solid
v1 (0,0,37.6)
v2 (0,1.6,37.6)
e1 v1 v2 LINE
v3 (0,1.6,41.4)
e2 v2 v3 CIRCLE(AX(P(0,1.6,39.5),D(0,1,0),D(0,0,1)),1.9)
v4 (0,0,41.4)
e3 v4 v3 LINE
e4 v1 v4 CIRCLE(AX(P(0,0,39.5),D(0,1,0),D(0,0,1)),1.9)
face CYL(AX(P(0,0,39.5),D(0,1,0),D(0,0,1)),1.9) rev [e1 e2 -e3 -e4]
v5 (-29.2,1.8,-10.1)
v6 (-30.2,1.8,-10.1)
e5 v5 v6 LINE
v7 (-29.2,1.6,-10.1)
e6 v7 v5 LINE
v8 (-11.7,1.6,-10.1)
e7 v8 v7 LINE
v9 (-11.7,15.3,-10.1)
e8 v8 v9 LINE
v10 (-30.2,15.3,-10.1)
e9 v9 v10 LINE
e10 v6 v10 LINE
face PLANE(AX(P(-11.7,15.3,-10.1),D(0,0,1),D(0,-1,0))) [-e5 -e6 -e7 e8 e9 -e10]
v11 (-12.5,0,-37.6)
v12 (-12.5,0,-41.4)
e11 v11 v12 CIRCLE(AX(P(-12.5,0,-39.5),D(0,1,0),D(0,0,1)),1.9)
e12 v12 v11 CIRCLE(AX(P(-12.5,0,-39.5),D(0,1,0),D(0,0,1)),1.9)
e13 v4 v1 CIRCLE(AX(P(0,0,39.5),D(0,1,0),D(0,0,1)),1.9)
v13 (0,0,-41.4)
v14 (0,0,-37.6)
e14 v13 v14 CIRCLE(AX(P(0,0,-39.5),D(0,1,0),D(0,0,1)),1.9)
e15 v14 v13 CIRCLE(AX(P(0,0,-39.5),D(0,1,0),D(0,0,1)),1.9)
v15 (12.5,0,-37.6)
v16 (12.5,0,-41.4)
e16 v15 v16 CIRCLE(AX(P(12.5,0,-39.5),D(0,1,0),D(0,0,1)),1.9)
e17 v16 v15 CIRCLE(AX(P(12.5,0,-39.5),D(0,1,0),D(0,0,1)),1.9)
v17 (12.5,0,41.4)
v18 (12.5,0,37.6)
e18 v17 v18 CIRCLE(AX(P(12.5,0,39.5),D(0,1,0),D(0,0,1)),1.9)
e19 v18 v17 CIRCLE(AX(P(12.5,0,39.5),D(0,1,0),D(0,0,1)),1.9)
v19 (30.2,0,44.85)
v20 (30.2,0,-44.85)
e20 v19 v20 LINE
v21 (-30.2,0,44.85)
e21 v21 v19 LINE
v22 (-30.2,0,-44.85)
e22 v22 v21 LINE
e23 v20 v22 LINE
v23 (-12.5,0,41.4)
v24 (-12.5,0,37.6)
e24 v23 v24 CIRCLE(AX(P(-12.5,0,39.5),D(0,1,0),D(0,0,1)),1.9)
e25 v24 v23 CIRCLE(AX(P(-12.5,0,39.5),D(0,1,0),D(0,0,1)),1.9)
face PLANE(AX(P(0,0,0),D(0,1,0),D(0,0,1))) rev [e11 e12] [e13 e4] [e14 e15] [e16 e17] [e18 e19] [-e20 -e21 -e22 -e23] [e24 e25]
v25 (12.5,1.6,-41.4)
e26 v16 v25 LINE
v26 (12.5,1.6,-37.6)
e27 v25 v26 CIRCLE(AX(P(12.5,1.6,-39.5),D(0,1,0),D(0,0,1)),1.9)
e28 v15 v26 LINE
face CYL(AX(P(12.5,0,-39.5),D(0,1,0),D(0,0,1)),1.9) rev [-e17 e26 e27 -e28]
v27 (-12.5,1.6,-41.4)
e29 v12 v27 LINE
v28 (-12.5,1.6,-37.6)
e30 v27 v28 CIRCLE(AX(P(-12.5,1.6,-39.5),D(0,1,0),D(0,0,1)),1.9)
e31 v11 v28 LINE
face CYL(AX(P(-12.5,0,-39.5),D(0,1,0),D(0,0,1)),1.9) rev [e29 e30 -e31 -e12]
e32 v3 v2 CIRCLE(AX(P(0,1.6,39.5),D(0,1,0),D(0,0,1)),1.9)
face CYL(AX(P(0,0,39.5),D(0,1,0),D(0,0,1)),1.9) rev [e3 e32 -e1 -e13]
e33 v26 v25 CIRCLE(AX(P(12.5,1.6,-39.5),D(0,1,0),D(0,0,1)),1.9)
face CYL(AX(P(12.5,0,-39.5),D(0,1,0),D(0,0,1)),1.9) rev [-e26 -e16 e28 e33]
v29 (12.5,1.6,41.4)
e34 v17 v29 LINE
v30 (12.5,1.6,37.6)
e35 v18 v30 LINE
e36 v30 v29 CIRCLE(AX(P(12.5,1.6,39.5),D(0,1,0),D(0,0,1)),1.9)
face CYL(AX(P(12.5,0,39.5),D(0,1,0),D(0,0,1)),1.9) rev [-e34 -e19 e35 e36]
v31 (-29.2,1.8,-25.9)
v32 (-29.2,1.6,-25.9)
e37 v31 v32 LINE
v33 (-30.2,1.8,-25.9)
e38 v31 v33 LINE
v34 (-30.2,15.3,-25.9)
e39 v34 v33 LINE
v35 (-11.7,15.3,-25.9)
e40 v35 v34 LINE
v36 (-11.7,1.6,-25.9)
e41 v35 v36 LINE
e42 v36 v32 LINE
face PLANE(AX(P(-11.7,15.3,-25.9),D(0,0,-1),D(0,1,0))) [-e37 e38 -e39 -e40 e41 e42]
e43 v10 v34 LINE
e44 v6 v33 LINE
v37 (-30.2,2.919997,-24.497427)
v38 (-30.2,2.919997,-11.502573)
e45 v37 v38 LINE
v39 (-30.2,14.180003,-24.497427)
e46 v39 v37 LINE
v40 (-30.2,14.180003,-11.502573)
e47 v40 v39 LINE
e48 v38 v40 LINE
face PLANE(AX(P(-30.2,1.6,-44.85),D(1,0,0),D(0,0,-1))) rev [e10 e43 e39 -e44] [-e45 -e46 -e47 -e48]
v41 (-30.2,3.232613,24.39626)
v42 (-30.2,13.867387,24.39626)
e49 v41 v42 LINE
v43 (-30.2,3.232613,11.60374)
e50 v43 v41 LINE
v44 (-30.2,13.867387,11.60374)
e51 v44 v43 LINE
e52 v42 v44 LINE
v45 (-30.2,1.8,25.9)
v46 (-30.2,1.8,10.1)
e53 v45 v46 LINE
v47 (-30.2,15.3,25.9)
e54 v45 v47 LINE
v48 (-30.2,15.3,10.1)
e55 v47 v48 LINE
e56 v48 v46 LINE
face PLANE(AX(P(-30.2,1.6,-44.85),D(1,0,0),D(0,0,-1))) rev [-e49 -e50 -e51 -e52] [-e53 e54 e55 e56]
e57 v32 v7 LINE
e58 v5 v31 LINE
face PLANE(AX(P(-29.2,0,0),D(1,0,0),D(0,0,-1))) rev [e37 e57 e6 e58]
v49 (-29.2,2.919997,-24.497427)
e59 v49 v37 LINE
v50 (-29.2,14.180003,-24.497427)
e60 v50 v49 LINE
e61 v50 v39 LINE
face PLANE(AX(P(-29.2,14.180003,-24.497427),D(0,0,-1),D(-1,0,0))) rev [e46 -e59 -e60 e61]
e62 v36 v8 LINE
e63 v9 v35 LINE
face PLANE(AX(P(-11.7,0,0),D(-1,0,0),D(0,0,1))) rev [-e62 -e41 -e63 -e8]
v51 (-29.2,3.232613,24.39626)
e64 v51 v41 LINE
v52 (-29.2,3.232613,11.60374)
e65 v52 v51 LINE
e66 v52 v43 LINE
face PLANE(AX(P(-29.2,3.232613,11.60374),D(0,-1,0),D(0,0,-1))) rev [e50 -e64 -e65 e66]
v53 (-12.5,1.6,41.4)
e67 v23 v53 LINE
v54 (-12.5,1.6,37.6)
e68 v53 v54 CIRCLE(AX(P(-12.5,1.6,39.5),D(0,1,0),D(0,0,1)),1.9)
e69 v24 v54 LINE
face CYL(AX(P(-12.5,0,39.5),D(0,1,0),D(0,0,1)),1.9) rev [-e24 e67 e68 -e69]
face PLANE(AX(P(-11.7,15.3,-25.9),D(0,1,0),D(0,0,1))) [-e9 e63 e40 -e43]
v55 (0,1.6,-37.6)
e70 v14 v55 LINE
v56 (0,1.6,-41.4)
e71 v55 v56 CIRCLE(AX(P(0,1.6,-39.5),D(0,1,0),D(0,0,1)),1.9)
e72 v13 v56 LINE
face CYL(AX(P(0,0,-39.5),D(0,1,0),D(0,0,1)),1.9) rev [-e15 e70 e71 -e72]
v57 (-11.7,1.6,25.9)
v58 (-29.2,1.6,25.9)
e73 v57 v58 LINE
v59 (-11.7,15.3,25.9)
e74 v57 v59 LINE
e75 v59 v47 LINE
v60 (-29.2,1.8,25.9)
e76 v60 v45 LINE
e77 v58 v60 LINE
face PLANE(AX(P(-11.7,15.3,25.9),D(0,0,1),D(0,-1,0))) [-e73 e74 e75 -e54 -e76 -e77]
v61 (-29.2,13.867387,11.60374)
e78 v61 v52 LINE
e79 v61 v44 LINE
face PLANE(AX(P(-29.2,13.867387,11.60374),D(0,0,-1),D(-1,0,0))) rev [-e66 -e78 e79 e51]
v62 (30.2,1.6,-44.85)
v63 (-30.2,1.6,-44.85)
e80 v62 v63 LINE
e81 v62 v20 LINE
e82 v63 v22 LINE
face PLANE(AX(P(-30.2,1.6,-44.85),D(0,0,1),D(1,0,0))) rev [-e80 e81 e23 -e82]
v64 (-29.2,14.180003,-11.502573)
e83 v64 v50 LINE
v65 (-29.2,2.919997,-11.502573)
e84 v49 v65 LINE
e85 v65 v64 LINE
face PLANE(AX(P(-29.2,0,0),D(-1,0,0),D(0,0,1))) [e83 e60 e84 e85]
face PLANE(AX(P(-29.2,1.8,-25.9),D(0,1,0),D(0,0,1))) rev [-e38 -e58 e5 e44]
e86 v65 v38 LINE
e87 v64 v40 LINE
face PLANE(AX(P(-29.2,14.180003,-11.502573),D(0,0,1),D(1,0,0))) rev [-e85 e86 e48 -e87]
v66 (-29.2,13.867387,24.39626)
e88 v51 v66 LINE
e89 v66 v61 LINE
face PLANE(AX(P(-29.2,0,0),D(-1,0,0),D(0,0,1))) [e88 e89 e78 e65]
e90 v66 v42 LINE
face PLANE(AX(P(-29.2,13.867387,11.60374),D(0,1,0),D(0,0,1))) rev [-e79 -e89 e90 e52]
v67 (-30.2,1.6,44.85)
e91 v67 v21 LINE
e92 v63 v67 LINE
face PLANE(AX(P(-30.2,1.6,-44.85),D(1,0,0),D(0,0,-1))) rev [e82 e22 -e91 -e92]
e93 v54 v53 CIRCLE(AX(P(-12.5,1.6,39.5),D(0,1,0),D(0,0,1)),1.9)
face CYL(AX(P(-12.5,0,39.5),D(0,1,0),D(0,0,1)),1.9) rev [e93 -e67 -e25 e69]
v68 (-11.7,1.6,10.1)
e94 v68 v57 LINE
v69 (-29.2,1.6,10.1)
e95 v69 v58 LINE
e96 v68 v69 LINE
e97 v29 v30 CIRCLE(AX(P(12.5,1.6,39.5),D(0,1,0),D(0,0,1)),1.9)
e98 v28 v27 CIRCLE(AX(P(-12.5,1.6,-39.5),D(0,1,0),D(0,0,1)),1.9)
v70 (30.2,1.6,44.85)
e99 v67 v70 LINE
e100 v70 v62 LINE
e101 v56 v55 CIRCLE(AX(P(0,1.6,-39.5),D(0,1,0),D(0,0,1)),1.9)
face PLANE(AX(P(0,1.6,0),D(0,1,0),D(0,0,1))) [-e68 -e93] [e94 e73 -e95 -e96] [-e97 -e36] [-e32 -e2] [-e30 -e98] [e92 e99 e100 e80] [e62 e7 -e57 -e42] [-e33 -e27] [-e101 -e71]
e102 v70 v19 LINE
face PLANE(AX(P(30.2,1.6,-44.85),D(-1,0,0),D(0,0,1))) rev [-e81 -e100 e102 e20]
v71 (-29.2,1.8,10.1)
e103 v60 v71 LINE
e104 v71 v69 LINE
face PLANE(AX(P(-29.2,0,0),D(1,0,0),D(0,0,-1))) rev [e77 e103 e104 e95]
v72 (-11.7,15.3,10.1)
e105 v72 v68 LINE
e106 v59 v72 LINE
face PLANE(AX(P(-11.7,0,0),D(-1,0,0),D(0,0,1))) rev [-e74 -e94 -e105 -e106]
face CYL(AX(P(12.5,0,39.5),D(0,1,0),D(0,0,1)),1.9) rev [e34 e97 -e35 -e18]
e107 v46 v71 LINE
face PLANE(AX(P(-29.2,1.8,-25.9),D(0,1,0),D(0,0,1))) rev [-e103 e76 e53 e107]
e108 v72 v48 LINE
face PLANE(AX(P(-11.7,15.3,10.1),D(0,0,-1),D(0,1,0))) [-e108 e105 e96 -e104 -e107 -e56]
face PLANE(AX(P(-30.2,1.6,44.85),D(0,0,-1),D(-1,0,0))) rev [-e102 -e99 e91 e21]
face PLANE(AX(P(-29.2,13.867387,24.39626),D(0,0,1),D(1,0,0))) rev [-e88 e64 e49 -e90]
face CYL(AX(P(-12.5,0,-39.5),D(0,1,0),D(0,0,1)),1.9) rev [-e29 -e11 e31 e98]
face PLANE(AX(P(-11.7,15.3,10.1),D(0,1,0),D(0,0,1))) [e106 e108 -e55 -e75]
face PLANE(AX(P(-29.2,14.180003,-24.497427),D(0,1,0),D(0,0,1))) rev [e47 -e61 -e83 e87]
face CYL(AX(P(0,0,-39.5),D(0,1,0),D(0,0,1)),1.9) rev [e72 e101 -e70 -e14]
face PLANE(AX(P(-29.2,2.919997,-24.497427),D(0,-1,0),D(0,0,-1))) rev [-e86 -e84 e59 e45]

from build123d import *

# Parameters (mm, degrees)
SKETCH_1_W          = 60.4
SKETCH_1_H          = 89.7
EXTRUDE_1_DEPTH     = 1.6
SKETCH_2_R          = 1.9
CUT_EXTRUDE_1_DEPTH = 1.6
SKETCH_3_W          = 15.8
SKETCH_3_H          = 13.7
EXTRUDE_2_DEPTH     = 18.5
SKETCH_4_W          = 51.8
SKETCH_4_H          = 0.2
CUT_EXTRUDE_2_DEPTH = 1
SKETCH_5_W          = 12.792520148
SKETCH_5_H          = 10.634773198
SKETCH_5_W_2        = 12.994853118
SKETCH_5_H_2        = 11.260006872
CUT_EXTRUDE_3_DEPTH = 1


with BuildPart() as part:
    # 草图1 → 凸台-拉伸1 (new body)
    with BuildSketch(Plane(origin=(0, 0, 0), x_dir=(1, 0, 0), z_dir=(0, 1, 0))):
        Rectangle(SKETCH_1_W, SKETCH_1_H)
    extrude(amount=EXTRUDE_1_DEPTH)

    # 草图2 → 切除-拉伸1 (cut)
    with BuildSketch(Plane(origin=(0, 1.6, 0), x_dir=(1, 0, 0), z_dir=(0, 1, 0))):
        with Locations(Location((-12.5, -39.5, 0), (0, 0, 270))):
            Circle(SKETCH_2_R)
        with Locations(Location((12.5, -39.5, 0), (0, 0, 270))):
            Circle(SKETCH_2_R)
        with Locations(Location((-12.5, 39.5, 0), (0, 0, 270))):
            Circle(SKETCH_2_R)
        with Locations(Location((12.5, 39.5, 0), (0, 0, 270))):
            Circle(SKETCH_2_R)
        with Locations(Location((0, 39.5, 0), (0, 0, 270))):
            Circle(SKETCH_2_R)
        with Locations(Location((0, -39.5, 0), (0, 0, 270))):
            Circle(SKETCH_2_R)
    extrude(amount=-CUT_EXTRUDE_1_DEPTH, mode=Mode.SUBTRACT)

    # 草图3 → 凸台-拉伸2 (add)
    with BuildSketch(Plane.ZY.offset(30.2)):
        with Locations((18, 8.45)):
            Rectangle(SKETCH_3_W, SKETCH_3_H)
        with Locations((-18, 8.45)):
            Rectangle(SKETCH_3_W, SKETCH_3_H)
    extrude(amount=-EXTRUDE_2_DEPTH)

    # 草图4 → 切除-拉伸2 (cut)
    with BuildSketch(Plane.ZY.offset(30.2)):
        with Locations((0, 1.7)):
            Rectangle(SKETCH_4_W, SKETCH_4_H)
    extrude(amount=-CUT_EXTRUDE_2_DEPTH, mode=Mode.SUBTRACT)

    # 草图5 → 切除-拉伸3 (cut)
    with BuildSketch(Plane.ZY.offset(30.2)):
        with Locations((18, 8.55)):
            Rectangle(SKETCH_5_W, SKETCH_5_H)
        with Locations((-18, 8.55)):
            Rectangle(SKETCH_5_W_2, SKETCH_5_H_2)
    extrude(amount=-CUT_EXTRUDE_3_DEPTH, mode=Mode.SUBTRACT)


solid = part.part
